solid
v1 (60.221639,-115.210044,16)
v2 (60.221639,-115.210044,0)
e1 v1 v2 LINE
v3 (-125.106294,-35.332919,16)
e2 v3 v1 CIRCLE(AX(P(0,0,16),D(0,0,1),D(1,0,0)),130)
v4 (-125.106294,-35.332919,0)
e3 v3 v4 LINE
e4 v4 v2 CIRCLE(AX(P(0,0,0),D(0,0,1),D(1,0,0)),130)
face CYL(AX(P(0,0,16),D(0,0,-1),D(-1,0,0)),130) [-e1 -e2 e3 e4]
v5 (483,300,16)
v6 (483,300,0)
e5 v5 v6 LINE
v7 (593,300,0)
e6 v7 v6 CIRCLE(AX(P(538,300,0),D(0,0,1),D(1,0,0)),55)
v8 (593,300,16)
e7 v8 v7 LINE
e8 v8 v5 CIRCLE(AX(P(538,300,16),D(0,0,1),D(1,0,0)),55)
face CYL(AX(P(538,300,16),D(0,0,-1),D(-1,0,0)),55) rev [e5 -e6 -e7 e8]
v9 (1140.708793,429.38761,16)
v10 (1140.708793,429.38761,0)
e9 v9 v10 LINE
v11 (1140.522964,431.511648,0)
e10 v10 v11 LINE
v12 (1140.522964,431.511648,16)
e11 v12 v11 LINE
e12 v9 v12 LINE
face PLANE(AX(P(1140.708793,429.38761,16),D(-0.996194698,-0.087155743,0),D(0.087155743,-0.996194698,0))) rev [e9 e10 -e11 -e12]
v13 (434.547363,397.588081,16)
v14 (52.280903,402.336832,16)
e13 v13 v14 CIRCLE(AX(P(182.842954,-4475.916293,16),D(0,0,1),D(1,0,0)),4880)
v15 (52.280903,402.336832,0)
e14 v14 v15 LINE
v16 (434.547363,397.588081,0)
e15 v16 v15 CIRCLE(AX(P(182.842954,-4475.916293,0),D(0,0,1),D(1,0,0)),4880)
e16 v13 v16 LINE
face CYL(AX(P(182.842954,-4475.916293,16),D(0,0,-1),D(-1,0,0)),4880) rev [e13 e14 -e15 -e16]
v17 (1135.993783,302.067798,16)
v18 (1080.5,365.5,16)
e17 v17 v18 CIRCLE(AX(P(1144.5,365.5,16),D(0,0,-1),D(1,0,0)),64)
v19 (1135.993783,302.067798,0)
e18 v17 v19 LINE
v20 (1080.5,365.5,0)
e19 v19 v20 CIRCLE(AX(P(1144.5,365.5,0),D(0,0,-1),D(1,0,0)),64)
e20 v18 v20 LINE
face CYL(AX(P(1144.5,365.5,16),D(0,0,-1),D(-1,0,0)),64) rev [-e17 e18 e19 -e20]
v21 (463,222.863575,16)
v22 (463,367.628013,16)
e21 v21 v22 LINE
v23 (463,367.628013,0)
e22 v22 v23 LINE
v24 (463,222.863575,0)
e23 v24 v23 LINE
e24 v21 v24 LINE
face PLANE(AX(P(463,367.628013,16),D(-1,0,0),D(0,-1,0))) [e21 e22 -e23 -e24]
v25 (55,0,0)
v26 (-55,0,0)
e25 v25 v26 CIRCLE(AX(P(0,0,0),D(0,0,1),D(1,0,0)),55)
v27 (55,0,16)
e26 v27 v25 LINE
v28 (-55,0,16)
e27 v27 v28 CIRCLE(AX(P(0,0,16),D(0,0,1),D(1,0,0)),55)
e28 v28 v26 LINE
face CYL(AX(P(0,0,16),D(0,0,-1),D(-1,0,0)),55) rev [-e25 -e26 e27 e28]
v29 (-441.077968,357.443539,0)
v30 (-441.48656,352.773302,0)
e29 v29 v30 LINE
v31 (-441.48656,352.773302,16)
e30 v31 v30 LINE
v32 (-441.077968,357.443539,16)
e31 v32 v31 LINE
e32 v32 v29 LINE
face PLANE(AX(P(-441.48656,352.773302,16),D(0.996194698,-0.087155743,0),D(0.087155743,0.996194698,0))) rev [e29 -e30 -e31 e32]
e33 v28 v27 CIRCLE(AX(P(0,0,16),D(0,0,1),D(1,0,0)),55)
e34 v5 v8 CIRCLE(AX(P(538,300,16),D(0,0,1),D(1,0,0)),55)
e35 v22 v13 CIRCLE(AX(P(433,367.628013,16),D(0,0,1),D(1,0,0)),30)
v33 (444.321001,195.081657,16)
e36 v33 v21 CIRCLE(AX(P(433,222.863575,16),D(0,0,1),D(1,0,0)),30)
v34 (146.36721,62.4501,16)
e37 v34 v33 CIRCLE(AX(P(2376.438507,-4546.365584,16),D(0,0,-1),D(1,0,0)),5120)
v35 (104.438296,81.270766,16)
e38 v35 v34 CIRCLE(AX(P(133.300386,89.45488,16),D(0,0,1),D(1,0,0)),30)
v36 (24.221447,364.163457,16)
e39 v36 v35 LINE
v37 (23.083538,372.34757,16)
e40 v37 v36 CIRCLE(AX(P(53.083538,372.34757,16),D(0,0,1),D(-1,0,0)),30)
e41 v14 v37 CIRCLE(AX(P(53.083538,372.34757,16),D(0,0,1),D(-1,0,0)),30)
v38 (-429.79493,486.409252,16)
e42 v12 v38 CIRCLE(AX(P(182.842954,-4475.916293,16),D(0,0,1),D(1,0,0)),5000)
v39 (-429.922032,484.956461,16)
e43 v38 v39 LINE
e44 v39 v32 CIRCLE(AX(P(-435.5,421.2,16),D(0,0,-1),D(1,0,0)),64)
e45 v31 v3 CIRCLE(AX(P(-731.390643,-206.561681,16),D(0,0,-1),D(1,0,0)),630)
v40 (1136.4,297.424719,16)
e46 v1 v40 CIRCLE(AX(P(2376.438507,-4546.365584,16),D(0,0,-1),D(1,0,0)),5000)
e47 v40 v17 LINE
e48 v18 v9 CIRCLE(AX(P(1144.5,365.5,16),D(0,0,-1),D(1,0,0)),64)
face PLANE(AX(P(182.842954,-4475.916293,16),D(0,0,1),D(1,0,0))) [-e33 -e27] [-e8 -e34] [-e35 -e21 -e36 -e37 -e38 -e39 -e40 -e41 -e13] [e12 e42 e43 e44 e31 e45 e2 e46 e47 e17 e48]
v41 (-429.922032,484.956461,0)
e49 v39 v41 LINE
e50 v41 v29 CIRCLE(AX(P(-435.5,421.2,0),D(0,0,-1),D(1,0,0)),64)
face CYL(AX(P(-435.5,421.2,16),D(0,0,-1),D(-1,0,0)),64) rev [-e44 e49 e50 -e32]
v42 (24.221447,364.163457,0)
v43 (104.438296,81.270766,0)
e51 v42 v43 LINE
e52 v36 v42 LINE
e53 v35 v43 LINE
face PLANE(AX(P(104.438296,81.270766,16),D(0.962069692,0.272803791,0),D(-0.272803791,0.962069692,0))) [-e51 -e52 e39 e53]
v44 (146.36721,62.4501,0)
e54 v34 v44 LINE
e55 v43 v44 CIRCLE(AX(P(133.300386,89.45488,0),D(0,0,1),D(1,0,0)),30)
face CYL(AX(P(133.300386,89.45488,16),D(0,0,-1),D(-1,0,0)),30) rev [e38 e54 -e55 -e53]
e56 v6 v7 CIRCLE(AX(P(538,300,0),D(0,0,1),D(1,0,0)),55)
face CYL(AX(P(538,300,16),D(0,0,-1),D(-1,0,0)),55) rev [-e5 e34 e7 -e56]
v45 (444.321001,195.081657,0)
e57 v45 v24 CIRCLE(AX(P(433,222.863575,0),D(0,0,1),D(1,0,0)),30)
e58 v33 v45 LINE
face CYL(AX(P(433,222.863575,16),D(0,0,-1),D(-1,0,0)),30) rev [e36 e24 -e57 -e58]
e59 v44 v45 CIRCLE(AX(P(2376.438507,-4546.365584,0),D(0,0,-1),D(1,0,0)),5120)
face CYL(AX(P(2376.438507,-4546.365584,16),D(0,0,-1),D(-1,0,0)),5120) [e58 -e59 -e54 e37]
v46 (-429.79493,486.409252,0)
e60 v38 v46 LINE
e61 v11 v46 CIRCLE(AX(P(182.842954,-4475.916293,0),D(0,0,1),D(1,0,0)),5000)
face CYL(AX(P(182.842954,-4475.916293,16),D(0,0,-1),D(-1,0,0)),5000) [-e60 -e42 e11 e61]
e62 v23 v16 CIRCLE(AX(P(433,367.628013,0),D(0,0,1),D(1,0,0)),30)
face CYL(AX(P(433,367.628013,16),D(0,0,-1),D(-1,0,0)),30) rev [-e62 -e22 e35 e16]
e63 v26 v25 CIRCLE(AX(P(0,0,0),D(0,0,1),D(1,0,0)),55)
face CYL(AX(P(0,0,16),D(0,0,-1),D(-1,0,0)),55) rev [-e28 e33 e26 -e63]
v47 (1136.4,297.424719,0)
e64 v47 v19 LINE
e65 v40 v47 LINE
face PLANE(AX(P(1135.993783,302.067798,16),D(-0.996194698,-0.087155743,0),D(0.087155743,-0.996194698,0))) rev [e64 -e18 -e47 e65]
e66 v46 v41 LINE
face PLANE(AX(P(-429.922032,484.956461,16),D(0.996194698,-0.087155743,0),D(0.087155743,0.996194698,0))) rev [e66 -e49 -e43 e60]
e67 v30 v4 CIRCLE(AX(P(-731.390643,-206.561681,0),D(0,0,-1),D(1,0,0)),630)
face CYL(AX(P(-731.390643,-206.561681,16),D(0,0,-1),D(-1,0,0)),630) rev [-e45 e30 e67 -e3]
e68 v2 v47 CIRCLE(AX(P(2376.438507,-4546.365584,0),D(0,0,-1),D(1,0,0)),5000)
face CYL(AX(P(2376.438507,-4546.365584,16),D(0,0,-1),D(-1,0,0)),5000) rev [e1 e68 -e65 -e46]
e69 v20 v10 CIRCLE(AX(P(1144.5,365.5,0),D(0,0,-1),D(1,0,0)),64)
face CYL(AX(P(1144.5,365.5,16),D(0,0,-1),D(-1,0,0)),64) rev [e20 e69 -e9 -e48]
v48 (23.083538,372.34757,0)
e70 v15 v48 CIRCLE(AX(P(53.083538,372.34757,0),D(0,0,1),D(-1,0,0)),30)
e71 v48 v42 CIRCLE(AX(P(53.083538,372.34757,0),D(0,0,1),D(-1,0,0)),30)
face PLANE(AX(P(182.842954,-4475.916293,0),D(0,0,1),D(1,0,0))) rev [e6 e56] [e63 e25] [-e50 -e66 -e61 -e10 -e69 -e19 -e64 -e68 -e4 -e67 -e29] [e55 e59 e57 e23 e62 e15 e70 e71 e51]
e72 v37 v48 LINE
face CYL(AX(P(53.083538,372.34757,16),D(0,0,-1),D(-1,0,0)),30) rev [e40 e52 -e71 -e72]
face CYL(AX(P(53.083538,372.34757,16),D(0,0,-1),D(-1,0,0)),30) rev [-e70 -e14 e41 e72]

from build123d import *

# Parameters (mm, degrees)
SKETCH1_R           = 55
BOSS_EXTRUDE1_DEPTH = 16


with BuildPart() as part:
    # Sketch1 → Boss-Extrude1 (new body)
    with BuildSketch(Plane.XY):
        with BuildLine():
            Line((-441.486560332, 352.773302295), (-441.077967536, 357.443539322))
            ThreePointArc((-441.077967536, 357.443539322), (-371.743539322, 415.622032464), (-429.922032464, 484.956460678))
            Line((-429.922032464, 484.956460678), (-429.79492965, 486.409252487))
            ThreePointArc((-429.79492965, 486.409252487), (357.533978136, 521.031079354), (1140.522963582, 431.511647932))
            Line((1140.522963582, 431.511647932), (1140.708792797, 429.387610285))
            ThreePointArc((1140.708792797, 429.387610285), (1080.543840624, 367.868475852), (1135.99378326, 302.067797793))
            Line((1135.99378326, 302.067797793), (1136.4, 297.424719211))
            ThreePointArc((1136.4, 297.424719211), (586.381263284, 122.220397305), (60.221638572, -115.21004404))
            ThreePointArc((60.221638572, -115.21004404), (-51.454770489, -119.38344355), (-125.106294133, -35.332919047))
            ThreePointArc((-125.106294133, -35.332919047), (-243.082301892, 191.502339862), (-441.486560332, 352.773302295))
        make_face()
        Circle(SKETCH1_R, mode=Mode.SUBTRACT)
        with Locations((538, 300)):
            Circle(SKETCH1_R, mode=Mode.SUBTRACT)
        with BuildLine():
            Line((463, 367.628013441), (463, 222.86357491))
            ThreePointArc((463, 222.86357491), (457.896084334, 206.124847813), (444.32100101, 195.08165748))
            ThreePointArc((444.32100101, 195.08165748), (294.287770433, 131.138912095), (146.367210305, 62.450100371))
            ThreePointArc((146.367210305, 62.450100371), (121.015152193, 62.085681339), (104.438295549, 81.270766055))
            Line((104.438295549, 81.270766055), (24.221447422, 364.163456776))
            ThreePointArc((24.221447422, 364.163456776), (28.91122692, 390.115501396), (52.280902613, 402.336831507))
            ThreePointArc((52.280902613, 402.336831507), (243.460652484, 403.707205867), (434.547363171, 397.588081319))
            ThreePointArc((434.547363171, 397.588081319), (454.753400827, 388.286898998), (463, 367.628013441))
        make_face(mode=Mode.SUBTRACT)
    extrude(amount=BOSS_EXTRUDE1_DEPTH)


solid = part.part
